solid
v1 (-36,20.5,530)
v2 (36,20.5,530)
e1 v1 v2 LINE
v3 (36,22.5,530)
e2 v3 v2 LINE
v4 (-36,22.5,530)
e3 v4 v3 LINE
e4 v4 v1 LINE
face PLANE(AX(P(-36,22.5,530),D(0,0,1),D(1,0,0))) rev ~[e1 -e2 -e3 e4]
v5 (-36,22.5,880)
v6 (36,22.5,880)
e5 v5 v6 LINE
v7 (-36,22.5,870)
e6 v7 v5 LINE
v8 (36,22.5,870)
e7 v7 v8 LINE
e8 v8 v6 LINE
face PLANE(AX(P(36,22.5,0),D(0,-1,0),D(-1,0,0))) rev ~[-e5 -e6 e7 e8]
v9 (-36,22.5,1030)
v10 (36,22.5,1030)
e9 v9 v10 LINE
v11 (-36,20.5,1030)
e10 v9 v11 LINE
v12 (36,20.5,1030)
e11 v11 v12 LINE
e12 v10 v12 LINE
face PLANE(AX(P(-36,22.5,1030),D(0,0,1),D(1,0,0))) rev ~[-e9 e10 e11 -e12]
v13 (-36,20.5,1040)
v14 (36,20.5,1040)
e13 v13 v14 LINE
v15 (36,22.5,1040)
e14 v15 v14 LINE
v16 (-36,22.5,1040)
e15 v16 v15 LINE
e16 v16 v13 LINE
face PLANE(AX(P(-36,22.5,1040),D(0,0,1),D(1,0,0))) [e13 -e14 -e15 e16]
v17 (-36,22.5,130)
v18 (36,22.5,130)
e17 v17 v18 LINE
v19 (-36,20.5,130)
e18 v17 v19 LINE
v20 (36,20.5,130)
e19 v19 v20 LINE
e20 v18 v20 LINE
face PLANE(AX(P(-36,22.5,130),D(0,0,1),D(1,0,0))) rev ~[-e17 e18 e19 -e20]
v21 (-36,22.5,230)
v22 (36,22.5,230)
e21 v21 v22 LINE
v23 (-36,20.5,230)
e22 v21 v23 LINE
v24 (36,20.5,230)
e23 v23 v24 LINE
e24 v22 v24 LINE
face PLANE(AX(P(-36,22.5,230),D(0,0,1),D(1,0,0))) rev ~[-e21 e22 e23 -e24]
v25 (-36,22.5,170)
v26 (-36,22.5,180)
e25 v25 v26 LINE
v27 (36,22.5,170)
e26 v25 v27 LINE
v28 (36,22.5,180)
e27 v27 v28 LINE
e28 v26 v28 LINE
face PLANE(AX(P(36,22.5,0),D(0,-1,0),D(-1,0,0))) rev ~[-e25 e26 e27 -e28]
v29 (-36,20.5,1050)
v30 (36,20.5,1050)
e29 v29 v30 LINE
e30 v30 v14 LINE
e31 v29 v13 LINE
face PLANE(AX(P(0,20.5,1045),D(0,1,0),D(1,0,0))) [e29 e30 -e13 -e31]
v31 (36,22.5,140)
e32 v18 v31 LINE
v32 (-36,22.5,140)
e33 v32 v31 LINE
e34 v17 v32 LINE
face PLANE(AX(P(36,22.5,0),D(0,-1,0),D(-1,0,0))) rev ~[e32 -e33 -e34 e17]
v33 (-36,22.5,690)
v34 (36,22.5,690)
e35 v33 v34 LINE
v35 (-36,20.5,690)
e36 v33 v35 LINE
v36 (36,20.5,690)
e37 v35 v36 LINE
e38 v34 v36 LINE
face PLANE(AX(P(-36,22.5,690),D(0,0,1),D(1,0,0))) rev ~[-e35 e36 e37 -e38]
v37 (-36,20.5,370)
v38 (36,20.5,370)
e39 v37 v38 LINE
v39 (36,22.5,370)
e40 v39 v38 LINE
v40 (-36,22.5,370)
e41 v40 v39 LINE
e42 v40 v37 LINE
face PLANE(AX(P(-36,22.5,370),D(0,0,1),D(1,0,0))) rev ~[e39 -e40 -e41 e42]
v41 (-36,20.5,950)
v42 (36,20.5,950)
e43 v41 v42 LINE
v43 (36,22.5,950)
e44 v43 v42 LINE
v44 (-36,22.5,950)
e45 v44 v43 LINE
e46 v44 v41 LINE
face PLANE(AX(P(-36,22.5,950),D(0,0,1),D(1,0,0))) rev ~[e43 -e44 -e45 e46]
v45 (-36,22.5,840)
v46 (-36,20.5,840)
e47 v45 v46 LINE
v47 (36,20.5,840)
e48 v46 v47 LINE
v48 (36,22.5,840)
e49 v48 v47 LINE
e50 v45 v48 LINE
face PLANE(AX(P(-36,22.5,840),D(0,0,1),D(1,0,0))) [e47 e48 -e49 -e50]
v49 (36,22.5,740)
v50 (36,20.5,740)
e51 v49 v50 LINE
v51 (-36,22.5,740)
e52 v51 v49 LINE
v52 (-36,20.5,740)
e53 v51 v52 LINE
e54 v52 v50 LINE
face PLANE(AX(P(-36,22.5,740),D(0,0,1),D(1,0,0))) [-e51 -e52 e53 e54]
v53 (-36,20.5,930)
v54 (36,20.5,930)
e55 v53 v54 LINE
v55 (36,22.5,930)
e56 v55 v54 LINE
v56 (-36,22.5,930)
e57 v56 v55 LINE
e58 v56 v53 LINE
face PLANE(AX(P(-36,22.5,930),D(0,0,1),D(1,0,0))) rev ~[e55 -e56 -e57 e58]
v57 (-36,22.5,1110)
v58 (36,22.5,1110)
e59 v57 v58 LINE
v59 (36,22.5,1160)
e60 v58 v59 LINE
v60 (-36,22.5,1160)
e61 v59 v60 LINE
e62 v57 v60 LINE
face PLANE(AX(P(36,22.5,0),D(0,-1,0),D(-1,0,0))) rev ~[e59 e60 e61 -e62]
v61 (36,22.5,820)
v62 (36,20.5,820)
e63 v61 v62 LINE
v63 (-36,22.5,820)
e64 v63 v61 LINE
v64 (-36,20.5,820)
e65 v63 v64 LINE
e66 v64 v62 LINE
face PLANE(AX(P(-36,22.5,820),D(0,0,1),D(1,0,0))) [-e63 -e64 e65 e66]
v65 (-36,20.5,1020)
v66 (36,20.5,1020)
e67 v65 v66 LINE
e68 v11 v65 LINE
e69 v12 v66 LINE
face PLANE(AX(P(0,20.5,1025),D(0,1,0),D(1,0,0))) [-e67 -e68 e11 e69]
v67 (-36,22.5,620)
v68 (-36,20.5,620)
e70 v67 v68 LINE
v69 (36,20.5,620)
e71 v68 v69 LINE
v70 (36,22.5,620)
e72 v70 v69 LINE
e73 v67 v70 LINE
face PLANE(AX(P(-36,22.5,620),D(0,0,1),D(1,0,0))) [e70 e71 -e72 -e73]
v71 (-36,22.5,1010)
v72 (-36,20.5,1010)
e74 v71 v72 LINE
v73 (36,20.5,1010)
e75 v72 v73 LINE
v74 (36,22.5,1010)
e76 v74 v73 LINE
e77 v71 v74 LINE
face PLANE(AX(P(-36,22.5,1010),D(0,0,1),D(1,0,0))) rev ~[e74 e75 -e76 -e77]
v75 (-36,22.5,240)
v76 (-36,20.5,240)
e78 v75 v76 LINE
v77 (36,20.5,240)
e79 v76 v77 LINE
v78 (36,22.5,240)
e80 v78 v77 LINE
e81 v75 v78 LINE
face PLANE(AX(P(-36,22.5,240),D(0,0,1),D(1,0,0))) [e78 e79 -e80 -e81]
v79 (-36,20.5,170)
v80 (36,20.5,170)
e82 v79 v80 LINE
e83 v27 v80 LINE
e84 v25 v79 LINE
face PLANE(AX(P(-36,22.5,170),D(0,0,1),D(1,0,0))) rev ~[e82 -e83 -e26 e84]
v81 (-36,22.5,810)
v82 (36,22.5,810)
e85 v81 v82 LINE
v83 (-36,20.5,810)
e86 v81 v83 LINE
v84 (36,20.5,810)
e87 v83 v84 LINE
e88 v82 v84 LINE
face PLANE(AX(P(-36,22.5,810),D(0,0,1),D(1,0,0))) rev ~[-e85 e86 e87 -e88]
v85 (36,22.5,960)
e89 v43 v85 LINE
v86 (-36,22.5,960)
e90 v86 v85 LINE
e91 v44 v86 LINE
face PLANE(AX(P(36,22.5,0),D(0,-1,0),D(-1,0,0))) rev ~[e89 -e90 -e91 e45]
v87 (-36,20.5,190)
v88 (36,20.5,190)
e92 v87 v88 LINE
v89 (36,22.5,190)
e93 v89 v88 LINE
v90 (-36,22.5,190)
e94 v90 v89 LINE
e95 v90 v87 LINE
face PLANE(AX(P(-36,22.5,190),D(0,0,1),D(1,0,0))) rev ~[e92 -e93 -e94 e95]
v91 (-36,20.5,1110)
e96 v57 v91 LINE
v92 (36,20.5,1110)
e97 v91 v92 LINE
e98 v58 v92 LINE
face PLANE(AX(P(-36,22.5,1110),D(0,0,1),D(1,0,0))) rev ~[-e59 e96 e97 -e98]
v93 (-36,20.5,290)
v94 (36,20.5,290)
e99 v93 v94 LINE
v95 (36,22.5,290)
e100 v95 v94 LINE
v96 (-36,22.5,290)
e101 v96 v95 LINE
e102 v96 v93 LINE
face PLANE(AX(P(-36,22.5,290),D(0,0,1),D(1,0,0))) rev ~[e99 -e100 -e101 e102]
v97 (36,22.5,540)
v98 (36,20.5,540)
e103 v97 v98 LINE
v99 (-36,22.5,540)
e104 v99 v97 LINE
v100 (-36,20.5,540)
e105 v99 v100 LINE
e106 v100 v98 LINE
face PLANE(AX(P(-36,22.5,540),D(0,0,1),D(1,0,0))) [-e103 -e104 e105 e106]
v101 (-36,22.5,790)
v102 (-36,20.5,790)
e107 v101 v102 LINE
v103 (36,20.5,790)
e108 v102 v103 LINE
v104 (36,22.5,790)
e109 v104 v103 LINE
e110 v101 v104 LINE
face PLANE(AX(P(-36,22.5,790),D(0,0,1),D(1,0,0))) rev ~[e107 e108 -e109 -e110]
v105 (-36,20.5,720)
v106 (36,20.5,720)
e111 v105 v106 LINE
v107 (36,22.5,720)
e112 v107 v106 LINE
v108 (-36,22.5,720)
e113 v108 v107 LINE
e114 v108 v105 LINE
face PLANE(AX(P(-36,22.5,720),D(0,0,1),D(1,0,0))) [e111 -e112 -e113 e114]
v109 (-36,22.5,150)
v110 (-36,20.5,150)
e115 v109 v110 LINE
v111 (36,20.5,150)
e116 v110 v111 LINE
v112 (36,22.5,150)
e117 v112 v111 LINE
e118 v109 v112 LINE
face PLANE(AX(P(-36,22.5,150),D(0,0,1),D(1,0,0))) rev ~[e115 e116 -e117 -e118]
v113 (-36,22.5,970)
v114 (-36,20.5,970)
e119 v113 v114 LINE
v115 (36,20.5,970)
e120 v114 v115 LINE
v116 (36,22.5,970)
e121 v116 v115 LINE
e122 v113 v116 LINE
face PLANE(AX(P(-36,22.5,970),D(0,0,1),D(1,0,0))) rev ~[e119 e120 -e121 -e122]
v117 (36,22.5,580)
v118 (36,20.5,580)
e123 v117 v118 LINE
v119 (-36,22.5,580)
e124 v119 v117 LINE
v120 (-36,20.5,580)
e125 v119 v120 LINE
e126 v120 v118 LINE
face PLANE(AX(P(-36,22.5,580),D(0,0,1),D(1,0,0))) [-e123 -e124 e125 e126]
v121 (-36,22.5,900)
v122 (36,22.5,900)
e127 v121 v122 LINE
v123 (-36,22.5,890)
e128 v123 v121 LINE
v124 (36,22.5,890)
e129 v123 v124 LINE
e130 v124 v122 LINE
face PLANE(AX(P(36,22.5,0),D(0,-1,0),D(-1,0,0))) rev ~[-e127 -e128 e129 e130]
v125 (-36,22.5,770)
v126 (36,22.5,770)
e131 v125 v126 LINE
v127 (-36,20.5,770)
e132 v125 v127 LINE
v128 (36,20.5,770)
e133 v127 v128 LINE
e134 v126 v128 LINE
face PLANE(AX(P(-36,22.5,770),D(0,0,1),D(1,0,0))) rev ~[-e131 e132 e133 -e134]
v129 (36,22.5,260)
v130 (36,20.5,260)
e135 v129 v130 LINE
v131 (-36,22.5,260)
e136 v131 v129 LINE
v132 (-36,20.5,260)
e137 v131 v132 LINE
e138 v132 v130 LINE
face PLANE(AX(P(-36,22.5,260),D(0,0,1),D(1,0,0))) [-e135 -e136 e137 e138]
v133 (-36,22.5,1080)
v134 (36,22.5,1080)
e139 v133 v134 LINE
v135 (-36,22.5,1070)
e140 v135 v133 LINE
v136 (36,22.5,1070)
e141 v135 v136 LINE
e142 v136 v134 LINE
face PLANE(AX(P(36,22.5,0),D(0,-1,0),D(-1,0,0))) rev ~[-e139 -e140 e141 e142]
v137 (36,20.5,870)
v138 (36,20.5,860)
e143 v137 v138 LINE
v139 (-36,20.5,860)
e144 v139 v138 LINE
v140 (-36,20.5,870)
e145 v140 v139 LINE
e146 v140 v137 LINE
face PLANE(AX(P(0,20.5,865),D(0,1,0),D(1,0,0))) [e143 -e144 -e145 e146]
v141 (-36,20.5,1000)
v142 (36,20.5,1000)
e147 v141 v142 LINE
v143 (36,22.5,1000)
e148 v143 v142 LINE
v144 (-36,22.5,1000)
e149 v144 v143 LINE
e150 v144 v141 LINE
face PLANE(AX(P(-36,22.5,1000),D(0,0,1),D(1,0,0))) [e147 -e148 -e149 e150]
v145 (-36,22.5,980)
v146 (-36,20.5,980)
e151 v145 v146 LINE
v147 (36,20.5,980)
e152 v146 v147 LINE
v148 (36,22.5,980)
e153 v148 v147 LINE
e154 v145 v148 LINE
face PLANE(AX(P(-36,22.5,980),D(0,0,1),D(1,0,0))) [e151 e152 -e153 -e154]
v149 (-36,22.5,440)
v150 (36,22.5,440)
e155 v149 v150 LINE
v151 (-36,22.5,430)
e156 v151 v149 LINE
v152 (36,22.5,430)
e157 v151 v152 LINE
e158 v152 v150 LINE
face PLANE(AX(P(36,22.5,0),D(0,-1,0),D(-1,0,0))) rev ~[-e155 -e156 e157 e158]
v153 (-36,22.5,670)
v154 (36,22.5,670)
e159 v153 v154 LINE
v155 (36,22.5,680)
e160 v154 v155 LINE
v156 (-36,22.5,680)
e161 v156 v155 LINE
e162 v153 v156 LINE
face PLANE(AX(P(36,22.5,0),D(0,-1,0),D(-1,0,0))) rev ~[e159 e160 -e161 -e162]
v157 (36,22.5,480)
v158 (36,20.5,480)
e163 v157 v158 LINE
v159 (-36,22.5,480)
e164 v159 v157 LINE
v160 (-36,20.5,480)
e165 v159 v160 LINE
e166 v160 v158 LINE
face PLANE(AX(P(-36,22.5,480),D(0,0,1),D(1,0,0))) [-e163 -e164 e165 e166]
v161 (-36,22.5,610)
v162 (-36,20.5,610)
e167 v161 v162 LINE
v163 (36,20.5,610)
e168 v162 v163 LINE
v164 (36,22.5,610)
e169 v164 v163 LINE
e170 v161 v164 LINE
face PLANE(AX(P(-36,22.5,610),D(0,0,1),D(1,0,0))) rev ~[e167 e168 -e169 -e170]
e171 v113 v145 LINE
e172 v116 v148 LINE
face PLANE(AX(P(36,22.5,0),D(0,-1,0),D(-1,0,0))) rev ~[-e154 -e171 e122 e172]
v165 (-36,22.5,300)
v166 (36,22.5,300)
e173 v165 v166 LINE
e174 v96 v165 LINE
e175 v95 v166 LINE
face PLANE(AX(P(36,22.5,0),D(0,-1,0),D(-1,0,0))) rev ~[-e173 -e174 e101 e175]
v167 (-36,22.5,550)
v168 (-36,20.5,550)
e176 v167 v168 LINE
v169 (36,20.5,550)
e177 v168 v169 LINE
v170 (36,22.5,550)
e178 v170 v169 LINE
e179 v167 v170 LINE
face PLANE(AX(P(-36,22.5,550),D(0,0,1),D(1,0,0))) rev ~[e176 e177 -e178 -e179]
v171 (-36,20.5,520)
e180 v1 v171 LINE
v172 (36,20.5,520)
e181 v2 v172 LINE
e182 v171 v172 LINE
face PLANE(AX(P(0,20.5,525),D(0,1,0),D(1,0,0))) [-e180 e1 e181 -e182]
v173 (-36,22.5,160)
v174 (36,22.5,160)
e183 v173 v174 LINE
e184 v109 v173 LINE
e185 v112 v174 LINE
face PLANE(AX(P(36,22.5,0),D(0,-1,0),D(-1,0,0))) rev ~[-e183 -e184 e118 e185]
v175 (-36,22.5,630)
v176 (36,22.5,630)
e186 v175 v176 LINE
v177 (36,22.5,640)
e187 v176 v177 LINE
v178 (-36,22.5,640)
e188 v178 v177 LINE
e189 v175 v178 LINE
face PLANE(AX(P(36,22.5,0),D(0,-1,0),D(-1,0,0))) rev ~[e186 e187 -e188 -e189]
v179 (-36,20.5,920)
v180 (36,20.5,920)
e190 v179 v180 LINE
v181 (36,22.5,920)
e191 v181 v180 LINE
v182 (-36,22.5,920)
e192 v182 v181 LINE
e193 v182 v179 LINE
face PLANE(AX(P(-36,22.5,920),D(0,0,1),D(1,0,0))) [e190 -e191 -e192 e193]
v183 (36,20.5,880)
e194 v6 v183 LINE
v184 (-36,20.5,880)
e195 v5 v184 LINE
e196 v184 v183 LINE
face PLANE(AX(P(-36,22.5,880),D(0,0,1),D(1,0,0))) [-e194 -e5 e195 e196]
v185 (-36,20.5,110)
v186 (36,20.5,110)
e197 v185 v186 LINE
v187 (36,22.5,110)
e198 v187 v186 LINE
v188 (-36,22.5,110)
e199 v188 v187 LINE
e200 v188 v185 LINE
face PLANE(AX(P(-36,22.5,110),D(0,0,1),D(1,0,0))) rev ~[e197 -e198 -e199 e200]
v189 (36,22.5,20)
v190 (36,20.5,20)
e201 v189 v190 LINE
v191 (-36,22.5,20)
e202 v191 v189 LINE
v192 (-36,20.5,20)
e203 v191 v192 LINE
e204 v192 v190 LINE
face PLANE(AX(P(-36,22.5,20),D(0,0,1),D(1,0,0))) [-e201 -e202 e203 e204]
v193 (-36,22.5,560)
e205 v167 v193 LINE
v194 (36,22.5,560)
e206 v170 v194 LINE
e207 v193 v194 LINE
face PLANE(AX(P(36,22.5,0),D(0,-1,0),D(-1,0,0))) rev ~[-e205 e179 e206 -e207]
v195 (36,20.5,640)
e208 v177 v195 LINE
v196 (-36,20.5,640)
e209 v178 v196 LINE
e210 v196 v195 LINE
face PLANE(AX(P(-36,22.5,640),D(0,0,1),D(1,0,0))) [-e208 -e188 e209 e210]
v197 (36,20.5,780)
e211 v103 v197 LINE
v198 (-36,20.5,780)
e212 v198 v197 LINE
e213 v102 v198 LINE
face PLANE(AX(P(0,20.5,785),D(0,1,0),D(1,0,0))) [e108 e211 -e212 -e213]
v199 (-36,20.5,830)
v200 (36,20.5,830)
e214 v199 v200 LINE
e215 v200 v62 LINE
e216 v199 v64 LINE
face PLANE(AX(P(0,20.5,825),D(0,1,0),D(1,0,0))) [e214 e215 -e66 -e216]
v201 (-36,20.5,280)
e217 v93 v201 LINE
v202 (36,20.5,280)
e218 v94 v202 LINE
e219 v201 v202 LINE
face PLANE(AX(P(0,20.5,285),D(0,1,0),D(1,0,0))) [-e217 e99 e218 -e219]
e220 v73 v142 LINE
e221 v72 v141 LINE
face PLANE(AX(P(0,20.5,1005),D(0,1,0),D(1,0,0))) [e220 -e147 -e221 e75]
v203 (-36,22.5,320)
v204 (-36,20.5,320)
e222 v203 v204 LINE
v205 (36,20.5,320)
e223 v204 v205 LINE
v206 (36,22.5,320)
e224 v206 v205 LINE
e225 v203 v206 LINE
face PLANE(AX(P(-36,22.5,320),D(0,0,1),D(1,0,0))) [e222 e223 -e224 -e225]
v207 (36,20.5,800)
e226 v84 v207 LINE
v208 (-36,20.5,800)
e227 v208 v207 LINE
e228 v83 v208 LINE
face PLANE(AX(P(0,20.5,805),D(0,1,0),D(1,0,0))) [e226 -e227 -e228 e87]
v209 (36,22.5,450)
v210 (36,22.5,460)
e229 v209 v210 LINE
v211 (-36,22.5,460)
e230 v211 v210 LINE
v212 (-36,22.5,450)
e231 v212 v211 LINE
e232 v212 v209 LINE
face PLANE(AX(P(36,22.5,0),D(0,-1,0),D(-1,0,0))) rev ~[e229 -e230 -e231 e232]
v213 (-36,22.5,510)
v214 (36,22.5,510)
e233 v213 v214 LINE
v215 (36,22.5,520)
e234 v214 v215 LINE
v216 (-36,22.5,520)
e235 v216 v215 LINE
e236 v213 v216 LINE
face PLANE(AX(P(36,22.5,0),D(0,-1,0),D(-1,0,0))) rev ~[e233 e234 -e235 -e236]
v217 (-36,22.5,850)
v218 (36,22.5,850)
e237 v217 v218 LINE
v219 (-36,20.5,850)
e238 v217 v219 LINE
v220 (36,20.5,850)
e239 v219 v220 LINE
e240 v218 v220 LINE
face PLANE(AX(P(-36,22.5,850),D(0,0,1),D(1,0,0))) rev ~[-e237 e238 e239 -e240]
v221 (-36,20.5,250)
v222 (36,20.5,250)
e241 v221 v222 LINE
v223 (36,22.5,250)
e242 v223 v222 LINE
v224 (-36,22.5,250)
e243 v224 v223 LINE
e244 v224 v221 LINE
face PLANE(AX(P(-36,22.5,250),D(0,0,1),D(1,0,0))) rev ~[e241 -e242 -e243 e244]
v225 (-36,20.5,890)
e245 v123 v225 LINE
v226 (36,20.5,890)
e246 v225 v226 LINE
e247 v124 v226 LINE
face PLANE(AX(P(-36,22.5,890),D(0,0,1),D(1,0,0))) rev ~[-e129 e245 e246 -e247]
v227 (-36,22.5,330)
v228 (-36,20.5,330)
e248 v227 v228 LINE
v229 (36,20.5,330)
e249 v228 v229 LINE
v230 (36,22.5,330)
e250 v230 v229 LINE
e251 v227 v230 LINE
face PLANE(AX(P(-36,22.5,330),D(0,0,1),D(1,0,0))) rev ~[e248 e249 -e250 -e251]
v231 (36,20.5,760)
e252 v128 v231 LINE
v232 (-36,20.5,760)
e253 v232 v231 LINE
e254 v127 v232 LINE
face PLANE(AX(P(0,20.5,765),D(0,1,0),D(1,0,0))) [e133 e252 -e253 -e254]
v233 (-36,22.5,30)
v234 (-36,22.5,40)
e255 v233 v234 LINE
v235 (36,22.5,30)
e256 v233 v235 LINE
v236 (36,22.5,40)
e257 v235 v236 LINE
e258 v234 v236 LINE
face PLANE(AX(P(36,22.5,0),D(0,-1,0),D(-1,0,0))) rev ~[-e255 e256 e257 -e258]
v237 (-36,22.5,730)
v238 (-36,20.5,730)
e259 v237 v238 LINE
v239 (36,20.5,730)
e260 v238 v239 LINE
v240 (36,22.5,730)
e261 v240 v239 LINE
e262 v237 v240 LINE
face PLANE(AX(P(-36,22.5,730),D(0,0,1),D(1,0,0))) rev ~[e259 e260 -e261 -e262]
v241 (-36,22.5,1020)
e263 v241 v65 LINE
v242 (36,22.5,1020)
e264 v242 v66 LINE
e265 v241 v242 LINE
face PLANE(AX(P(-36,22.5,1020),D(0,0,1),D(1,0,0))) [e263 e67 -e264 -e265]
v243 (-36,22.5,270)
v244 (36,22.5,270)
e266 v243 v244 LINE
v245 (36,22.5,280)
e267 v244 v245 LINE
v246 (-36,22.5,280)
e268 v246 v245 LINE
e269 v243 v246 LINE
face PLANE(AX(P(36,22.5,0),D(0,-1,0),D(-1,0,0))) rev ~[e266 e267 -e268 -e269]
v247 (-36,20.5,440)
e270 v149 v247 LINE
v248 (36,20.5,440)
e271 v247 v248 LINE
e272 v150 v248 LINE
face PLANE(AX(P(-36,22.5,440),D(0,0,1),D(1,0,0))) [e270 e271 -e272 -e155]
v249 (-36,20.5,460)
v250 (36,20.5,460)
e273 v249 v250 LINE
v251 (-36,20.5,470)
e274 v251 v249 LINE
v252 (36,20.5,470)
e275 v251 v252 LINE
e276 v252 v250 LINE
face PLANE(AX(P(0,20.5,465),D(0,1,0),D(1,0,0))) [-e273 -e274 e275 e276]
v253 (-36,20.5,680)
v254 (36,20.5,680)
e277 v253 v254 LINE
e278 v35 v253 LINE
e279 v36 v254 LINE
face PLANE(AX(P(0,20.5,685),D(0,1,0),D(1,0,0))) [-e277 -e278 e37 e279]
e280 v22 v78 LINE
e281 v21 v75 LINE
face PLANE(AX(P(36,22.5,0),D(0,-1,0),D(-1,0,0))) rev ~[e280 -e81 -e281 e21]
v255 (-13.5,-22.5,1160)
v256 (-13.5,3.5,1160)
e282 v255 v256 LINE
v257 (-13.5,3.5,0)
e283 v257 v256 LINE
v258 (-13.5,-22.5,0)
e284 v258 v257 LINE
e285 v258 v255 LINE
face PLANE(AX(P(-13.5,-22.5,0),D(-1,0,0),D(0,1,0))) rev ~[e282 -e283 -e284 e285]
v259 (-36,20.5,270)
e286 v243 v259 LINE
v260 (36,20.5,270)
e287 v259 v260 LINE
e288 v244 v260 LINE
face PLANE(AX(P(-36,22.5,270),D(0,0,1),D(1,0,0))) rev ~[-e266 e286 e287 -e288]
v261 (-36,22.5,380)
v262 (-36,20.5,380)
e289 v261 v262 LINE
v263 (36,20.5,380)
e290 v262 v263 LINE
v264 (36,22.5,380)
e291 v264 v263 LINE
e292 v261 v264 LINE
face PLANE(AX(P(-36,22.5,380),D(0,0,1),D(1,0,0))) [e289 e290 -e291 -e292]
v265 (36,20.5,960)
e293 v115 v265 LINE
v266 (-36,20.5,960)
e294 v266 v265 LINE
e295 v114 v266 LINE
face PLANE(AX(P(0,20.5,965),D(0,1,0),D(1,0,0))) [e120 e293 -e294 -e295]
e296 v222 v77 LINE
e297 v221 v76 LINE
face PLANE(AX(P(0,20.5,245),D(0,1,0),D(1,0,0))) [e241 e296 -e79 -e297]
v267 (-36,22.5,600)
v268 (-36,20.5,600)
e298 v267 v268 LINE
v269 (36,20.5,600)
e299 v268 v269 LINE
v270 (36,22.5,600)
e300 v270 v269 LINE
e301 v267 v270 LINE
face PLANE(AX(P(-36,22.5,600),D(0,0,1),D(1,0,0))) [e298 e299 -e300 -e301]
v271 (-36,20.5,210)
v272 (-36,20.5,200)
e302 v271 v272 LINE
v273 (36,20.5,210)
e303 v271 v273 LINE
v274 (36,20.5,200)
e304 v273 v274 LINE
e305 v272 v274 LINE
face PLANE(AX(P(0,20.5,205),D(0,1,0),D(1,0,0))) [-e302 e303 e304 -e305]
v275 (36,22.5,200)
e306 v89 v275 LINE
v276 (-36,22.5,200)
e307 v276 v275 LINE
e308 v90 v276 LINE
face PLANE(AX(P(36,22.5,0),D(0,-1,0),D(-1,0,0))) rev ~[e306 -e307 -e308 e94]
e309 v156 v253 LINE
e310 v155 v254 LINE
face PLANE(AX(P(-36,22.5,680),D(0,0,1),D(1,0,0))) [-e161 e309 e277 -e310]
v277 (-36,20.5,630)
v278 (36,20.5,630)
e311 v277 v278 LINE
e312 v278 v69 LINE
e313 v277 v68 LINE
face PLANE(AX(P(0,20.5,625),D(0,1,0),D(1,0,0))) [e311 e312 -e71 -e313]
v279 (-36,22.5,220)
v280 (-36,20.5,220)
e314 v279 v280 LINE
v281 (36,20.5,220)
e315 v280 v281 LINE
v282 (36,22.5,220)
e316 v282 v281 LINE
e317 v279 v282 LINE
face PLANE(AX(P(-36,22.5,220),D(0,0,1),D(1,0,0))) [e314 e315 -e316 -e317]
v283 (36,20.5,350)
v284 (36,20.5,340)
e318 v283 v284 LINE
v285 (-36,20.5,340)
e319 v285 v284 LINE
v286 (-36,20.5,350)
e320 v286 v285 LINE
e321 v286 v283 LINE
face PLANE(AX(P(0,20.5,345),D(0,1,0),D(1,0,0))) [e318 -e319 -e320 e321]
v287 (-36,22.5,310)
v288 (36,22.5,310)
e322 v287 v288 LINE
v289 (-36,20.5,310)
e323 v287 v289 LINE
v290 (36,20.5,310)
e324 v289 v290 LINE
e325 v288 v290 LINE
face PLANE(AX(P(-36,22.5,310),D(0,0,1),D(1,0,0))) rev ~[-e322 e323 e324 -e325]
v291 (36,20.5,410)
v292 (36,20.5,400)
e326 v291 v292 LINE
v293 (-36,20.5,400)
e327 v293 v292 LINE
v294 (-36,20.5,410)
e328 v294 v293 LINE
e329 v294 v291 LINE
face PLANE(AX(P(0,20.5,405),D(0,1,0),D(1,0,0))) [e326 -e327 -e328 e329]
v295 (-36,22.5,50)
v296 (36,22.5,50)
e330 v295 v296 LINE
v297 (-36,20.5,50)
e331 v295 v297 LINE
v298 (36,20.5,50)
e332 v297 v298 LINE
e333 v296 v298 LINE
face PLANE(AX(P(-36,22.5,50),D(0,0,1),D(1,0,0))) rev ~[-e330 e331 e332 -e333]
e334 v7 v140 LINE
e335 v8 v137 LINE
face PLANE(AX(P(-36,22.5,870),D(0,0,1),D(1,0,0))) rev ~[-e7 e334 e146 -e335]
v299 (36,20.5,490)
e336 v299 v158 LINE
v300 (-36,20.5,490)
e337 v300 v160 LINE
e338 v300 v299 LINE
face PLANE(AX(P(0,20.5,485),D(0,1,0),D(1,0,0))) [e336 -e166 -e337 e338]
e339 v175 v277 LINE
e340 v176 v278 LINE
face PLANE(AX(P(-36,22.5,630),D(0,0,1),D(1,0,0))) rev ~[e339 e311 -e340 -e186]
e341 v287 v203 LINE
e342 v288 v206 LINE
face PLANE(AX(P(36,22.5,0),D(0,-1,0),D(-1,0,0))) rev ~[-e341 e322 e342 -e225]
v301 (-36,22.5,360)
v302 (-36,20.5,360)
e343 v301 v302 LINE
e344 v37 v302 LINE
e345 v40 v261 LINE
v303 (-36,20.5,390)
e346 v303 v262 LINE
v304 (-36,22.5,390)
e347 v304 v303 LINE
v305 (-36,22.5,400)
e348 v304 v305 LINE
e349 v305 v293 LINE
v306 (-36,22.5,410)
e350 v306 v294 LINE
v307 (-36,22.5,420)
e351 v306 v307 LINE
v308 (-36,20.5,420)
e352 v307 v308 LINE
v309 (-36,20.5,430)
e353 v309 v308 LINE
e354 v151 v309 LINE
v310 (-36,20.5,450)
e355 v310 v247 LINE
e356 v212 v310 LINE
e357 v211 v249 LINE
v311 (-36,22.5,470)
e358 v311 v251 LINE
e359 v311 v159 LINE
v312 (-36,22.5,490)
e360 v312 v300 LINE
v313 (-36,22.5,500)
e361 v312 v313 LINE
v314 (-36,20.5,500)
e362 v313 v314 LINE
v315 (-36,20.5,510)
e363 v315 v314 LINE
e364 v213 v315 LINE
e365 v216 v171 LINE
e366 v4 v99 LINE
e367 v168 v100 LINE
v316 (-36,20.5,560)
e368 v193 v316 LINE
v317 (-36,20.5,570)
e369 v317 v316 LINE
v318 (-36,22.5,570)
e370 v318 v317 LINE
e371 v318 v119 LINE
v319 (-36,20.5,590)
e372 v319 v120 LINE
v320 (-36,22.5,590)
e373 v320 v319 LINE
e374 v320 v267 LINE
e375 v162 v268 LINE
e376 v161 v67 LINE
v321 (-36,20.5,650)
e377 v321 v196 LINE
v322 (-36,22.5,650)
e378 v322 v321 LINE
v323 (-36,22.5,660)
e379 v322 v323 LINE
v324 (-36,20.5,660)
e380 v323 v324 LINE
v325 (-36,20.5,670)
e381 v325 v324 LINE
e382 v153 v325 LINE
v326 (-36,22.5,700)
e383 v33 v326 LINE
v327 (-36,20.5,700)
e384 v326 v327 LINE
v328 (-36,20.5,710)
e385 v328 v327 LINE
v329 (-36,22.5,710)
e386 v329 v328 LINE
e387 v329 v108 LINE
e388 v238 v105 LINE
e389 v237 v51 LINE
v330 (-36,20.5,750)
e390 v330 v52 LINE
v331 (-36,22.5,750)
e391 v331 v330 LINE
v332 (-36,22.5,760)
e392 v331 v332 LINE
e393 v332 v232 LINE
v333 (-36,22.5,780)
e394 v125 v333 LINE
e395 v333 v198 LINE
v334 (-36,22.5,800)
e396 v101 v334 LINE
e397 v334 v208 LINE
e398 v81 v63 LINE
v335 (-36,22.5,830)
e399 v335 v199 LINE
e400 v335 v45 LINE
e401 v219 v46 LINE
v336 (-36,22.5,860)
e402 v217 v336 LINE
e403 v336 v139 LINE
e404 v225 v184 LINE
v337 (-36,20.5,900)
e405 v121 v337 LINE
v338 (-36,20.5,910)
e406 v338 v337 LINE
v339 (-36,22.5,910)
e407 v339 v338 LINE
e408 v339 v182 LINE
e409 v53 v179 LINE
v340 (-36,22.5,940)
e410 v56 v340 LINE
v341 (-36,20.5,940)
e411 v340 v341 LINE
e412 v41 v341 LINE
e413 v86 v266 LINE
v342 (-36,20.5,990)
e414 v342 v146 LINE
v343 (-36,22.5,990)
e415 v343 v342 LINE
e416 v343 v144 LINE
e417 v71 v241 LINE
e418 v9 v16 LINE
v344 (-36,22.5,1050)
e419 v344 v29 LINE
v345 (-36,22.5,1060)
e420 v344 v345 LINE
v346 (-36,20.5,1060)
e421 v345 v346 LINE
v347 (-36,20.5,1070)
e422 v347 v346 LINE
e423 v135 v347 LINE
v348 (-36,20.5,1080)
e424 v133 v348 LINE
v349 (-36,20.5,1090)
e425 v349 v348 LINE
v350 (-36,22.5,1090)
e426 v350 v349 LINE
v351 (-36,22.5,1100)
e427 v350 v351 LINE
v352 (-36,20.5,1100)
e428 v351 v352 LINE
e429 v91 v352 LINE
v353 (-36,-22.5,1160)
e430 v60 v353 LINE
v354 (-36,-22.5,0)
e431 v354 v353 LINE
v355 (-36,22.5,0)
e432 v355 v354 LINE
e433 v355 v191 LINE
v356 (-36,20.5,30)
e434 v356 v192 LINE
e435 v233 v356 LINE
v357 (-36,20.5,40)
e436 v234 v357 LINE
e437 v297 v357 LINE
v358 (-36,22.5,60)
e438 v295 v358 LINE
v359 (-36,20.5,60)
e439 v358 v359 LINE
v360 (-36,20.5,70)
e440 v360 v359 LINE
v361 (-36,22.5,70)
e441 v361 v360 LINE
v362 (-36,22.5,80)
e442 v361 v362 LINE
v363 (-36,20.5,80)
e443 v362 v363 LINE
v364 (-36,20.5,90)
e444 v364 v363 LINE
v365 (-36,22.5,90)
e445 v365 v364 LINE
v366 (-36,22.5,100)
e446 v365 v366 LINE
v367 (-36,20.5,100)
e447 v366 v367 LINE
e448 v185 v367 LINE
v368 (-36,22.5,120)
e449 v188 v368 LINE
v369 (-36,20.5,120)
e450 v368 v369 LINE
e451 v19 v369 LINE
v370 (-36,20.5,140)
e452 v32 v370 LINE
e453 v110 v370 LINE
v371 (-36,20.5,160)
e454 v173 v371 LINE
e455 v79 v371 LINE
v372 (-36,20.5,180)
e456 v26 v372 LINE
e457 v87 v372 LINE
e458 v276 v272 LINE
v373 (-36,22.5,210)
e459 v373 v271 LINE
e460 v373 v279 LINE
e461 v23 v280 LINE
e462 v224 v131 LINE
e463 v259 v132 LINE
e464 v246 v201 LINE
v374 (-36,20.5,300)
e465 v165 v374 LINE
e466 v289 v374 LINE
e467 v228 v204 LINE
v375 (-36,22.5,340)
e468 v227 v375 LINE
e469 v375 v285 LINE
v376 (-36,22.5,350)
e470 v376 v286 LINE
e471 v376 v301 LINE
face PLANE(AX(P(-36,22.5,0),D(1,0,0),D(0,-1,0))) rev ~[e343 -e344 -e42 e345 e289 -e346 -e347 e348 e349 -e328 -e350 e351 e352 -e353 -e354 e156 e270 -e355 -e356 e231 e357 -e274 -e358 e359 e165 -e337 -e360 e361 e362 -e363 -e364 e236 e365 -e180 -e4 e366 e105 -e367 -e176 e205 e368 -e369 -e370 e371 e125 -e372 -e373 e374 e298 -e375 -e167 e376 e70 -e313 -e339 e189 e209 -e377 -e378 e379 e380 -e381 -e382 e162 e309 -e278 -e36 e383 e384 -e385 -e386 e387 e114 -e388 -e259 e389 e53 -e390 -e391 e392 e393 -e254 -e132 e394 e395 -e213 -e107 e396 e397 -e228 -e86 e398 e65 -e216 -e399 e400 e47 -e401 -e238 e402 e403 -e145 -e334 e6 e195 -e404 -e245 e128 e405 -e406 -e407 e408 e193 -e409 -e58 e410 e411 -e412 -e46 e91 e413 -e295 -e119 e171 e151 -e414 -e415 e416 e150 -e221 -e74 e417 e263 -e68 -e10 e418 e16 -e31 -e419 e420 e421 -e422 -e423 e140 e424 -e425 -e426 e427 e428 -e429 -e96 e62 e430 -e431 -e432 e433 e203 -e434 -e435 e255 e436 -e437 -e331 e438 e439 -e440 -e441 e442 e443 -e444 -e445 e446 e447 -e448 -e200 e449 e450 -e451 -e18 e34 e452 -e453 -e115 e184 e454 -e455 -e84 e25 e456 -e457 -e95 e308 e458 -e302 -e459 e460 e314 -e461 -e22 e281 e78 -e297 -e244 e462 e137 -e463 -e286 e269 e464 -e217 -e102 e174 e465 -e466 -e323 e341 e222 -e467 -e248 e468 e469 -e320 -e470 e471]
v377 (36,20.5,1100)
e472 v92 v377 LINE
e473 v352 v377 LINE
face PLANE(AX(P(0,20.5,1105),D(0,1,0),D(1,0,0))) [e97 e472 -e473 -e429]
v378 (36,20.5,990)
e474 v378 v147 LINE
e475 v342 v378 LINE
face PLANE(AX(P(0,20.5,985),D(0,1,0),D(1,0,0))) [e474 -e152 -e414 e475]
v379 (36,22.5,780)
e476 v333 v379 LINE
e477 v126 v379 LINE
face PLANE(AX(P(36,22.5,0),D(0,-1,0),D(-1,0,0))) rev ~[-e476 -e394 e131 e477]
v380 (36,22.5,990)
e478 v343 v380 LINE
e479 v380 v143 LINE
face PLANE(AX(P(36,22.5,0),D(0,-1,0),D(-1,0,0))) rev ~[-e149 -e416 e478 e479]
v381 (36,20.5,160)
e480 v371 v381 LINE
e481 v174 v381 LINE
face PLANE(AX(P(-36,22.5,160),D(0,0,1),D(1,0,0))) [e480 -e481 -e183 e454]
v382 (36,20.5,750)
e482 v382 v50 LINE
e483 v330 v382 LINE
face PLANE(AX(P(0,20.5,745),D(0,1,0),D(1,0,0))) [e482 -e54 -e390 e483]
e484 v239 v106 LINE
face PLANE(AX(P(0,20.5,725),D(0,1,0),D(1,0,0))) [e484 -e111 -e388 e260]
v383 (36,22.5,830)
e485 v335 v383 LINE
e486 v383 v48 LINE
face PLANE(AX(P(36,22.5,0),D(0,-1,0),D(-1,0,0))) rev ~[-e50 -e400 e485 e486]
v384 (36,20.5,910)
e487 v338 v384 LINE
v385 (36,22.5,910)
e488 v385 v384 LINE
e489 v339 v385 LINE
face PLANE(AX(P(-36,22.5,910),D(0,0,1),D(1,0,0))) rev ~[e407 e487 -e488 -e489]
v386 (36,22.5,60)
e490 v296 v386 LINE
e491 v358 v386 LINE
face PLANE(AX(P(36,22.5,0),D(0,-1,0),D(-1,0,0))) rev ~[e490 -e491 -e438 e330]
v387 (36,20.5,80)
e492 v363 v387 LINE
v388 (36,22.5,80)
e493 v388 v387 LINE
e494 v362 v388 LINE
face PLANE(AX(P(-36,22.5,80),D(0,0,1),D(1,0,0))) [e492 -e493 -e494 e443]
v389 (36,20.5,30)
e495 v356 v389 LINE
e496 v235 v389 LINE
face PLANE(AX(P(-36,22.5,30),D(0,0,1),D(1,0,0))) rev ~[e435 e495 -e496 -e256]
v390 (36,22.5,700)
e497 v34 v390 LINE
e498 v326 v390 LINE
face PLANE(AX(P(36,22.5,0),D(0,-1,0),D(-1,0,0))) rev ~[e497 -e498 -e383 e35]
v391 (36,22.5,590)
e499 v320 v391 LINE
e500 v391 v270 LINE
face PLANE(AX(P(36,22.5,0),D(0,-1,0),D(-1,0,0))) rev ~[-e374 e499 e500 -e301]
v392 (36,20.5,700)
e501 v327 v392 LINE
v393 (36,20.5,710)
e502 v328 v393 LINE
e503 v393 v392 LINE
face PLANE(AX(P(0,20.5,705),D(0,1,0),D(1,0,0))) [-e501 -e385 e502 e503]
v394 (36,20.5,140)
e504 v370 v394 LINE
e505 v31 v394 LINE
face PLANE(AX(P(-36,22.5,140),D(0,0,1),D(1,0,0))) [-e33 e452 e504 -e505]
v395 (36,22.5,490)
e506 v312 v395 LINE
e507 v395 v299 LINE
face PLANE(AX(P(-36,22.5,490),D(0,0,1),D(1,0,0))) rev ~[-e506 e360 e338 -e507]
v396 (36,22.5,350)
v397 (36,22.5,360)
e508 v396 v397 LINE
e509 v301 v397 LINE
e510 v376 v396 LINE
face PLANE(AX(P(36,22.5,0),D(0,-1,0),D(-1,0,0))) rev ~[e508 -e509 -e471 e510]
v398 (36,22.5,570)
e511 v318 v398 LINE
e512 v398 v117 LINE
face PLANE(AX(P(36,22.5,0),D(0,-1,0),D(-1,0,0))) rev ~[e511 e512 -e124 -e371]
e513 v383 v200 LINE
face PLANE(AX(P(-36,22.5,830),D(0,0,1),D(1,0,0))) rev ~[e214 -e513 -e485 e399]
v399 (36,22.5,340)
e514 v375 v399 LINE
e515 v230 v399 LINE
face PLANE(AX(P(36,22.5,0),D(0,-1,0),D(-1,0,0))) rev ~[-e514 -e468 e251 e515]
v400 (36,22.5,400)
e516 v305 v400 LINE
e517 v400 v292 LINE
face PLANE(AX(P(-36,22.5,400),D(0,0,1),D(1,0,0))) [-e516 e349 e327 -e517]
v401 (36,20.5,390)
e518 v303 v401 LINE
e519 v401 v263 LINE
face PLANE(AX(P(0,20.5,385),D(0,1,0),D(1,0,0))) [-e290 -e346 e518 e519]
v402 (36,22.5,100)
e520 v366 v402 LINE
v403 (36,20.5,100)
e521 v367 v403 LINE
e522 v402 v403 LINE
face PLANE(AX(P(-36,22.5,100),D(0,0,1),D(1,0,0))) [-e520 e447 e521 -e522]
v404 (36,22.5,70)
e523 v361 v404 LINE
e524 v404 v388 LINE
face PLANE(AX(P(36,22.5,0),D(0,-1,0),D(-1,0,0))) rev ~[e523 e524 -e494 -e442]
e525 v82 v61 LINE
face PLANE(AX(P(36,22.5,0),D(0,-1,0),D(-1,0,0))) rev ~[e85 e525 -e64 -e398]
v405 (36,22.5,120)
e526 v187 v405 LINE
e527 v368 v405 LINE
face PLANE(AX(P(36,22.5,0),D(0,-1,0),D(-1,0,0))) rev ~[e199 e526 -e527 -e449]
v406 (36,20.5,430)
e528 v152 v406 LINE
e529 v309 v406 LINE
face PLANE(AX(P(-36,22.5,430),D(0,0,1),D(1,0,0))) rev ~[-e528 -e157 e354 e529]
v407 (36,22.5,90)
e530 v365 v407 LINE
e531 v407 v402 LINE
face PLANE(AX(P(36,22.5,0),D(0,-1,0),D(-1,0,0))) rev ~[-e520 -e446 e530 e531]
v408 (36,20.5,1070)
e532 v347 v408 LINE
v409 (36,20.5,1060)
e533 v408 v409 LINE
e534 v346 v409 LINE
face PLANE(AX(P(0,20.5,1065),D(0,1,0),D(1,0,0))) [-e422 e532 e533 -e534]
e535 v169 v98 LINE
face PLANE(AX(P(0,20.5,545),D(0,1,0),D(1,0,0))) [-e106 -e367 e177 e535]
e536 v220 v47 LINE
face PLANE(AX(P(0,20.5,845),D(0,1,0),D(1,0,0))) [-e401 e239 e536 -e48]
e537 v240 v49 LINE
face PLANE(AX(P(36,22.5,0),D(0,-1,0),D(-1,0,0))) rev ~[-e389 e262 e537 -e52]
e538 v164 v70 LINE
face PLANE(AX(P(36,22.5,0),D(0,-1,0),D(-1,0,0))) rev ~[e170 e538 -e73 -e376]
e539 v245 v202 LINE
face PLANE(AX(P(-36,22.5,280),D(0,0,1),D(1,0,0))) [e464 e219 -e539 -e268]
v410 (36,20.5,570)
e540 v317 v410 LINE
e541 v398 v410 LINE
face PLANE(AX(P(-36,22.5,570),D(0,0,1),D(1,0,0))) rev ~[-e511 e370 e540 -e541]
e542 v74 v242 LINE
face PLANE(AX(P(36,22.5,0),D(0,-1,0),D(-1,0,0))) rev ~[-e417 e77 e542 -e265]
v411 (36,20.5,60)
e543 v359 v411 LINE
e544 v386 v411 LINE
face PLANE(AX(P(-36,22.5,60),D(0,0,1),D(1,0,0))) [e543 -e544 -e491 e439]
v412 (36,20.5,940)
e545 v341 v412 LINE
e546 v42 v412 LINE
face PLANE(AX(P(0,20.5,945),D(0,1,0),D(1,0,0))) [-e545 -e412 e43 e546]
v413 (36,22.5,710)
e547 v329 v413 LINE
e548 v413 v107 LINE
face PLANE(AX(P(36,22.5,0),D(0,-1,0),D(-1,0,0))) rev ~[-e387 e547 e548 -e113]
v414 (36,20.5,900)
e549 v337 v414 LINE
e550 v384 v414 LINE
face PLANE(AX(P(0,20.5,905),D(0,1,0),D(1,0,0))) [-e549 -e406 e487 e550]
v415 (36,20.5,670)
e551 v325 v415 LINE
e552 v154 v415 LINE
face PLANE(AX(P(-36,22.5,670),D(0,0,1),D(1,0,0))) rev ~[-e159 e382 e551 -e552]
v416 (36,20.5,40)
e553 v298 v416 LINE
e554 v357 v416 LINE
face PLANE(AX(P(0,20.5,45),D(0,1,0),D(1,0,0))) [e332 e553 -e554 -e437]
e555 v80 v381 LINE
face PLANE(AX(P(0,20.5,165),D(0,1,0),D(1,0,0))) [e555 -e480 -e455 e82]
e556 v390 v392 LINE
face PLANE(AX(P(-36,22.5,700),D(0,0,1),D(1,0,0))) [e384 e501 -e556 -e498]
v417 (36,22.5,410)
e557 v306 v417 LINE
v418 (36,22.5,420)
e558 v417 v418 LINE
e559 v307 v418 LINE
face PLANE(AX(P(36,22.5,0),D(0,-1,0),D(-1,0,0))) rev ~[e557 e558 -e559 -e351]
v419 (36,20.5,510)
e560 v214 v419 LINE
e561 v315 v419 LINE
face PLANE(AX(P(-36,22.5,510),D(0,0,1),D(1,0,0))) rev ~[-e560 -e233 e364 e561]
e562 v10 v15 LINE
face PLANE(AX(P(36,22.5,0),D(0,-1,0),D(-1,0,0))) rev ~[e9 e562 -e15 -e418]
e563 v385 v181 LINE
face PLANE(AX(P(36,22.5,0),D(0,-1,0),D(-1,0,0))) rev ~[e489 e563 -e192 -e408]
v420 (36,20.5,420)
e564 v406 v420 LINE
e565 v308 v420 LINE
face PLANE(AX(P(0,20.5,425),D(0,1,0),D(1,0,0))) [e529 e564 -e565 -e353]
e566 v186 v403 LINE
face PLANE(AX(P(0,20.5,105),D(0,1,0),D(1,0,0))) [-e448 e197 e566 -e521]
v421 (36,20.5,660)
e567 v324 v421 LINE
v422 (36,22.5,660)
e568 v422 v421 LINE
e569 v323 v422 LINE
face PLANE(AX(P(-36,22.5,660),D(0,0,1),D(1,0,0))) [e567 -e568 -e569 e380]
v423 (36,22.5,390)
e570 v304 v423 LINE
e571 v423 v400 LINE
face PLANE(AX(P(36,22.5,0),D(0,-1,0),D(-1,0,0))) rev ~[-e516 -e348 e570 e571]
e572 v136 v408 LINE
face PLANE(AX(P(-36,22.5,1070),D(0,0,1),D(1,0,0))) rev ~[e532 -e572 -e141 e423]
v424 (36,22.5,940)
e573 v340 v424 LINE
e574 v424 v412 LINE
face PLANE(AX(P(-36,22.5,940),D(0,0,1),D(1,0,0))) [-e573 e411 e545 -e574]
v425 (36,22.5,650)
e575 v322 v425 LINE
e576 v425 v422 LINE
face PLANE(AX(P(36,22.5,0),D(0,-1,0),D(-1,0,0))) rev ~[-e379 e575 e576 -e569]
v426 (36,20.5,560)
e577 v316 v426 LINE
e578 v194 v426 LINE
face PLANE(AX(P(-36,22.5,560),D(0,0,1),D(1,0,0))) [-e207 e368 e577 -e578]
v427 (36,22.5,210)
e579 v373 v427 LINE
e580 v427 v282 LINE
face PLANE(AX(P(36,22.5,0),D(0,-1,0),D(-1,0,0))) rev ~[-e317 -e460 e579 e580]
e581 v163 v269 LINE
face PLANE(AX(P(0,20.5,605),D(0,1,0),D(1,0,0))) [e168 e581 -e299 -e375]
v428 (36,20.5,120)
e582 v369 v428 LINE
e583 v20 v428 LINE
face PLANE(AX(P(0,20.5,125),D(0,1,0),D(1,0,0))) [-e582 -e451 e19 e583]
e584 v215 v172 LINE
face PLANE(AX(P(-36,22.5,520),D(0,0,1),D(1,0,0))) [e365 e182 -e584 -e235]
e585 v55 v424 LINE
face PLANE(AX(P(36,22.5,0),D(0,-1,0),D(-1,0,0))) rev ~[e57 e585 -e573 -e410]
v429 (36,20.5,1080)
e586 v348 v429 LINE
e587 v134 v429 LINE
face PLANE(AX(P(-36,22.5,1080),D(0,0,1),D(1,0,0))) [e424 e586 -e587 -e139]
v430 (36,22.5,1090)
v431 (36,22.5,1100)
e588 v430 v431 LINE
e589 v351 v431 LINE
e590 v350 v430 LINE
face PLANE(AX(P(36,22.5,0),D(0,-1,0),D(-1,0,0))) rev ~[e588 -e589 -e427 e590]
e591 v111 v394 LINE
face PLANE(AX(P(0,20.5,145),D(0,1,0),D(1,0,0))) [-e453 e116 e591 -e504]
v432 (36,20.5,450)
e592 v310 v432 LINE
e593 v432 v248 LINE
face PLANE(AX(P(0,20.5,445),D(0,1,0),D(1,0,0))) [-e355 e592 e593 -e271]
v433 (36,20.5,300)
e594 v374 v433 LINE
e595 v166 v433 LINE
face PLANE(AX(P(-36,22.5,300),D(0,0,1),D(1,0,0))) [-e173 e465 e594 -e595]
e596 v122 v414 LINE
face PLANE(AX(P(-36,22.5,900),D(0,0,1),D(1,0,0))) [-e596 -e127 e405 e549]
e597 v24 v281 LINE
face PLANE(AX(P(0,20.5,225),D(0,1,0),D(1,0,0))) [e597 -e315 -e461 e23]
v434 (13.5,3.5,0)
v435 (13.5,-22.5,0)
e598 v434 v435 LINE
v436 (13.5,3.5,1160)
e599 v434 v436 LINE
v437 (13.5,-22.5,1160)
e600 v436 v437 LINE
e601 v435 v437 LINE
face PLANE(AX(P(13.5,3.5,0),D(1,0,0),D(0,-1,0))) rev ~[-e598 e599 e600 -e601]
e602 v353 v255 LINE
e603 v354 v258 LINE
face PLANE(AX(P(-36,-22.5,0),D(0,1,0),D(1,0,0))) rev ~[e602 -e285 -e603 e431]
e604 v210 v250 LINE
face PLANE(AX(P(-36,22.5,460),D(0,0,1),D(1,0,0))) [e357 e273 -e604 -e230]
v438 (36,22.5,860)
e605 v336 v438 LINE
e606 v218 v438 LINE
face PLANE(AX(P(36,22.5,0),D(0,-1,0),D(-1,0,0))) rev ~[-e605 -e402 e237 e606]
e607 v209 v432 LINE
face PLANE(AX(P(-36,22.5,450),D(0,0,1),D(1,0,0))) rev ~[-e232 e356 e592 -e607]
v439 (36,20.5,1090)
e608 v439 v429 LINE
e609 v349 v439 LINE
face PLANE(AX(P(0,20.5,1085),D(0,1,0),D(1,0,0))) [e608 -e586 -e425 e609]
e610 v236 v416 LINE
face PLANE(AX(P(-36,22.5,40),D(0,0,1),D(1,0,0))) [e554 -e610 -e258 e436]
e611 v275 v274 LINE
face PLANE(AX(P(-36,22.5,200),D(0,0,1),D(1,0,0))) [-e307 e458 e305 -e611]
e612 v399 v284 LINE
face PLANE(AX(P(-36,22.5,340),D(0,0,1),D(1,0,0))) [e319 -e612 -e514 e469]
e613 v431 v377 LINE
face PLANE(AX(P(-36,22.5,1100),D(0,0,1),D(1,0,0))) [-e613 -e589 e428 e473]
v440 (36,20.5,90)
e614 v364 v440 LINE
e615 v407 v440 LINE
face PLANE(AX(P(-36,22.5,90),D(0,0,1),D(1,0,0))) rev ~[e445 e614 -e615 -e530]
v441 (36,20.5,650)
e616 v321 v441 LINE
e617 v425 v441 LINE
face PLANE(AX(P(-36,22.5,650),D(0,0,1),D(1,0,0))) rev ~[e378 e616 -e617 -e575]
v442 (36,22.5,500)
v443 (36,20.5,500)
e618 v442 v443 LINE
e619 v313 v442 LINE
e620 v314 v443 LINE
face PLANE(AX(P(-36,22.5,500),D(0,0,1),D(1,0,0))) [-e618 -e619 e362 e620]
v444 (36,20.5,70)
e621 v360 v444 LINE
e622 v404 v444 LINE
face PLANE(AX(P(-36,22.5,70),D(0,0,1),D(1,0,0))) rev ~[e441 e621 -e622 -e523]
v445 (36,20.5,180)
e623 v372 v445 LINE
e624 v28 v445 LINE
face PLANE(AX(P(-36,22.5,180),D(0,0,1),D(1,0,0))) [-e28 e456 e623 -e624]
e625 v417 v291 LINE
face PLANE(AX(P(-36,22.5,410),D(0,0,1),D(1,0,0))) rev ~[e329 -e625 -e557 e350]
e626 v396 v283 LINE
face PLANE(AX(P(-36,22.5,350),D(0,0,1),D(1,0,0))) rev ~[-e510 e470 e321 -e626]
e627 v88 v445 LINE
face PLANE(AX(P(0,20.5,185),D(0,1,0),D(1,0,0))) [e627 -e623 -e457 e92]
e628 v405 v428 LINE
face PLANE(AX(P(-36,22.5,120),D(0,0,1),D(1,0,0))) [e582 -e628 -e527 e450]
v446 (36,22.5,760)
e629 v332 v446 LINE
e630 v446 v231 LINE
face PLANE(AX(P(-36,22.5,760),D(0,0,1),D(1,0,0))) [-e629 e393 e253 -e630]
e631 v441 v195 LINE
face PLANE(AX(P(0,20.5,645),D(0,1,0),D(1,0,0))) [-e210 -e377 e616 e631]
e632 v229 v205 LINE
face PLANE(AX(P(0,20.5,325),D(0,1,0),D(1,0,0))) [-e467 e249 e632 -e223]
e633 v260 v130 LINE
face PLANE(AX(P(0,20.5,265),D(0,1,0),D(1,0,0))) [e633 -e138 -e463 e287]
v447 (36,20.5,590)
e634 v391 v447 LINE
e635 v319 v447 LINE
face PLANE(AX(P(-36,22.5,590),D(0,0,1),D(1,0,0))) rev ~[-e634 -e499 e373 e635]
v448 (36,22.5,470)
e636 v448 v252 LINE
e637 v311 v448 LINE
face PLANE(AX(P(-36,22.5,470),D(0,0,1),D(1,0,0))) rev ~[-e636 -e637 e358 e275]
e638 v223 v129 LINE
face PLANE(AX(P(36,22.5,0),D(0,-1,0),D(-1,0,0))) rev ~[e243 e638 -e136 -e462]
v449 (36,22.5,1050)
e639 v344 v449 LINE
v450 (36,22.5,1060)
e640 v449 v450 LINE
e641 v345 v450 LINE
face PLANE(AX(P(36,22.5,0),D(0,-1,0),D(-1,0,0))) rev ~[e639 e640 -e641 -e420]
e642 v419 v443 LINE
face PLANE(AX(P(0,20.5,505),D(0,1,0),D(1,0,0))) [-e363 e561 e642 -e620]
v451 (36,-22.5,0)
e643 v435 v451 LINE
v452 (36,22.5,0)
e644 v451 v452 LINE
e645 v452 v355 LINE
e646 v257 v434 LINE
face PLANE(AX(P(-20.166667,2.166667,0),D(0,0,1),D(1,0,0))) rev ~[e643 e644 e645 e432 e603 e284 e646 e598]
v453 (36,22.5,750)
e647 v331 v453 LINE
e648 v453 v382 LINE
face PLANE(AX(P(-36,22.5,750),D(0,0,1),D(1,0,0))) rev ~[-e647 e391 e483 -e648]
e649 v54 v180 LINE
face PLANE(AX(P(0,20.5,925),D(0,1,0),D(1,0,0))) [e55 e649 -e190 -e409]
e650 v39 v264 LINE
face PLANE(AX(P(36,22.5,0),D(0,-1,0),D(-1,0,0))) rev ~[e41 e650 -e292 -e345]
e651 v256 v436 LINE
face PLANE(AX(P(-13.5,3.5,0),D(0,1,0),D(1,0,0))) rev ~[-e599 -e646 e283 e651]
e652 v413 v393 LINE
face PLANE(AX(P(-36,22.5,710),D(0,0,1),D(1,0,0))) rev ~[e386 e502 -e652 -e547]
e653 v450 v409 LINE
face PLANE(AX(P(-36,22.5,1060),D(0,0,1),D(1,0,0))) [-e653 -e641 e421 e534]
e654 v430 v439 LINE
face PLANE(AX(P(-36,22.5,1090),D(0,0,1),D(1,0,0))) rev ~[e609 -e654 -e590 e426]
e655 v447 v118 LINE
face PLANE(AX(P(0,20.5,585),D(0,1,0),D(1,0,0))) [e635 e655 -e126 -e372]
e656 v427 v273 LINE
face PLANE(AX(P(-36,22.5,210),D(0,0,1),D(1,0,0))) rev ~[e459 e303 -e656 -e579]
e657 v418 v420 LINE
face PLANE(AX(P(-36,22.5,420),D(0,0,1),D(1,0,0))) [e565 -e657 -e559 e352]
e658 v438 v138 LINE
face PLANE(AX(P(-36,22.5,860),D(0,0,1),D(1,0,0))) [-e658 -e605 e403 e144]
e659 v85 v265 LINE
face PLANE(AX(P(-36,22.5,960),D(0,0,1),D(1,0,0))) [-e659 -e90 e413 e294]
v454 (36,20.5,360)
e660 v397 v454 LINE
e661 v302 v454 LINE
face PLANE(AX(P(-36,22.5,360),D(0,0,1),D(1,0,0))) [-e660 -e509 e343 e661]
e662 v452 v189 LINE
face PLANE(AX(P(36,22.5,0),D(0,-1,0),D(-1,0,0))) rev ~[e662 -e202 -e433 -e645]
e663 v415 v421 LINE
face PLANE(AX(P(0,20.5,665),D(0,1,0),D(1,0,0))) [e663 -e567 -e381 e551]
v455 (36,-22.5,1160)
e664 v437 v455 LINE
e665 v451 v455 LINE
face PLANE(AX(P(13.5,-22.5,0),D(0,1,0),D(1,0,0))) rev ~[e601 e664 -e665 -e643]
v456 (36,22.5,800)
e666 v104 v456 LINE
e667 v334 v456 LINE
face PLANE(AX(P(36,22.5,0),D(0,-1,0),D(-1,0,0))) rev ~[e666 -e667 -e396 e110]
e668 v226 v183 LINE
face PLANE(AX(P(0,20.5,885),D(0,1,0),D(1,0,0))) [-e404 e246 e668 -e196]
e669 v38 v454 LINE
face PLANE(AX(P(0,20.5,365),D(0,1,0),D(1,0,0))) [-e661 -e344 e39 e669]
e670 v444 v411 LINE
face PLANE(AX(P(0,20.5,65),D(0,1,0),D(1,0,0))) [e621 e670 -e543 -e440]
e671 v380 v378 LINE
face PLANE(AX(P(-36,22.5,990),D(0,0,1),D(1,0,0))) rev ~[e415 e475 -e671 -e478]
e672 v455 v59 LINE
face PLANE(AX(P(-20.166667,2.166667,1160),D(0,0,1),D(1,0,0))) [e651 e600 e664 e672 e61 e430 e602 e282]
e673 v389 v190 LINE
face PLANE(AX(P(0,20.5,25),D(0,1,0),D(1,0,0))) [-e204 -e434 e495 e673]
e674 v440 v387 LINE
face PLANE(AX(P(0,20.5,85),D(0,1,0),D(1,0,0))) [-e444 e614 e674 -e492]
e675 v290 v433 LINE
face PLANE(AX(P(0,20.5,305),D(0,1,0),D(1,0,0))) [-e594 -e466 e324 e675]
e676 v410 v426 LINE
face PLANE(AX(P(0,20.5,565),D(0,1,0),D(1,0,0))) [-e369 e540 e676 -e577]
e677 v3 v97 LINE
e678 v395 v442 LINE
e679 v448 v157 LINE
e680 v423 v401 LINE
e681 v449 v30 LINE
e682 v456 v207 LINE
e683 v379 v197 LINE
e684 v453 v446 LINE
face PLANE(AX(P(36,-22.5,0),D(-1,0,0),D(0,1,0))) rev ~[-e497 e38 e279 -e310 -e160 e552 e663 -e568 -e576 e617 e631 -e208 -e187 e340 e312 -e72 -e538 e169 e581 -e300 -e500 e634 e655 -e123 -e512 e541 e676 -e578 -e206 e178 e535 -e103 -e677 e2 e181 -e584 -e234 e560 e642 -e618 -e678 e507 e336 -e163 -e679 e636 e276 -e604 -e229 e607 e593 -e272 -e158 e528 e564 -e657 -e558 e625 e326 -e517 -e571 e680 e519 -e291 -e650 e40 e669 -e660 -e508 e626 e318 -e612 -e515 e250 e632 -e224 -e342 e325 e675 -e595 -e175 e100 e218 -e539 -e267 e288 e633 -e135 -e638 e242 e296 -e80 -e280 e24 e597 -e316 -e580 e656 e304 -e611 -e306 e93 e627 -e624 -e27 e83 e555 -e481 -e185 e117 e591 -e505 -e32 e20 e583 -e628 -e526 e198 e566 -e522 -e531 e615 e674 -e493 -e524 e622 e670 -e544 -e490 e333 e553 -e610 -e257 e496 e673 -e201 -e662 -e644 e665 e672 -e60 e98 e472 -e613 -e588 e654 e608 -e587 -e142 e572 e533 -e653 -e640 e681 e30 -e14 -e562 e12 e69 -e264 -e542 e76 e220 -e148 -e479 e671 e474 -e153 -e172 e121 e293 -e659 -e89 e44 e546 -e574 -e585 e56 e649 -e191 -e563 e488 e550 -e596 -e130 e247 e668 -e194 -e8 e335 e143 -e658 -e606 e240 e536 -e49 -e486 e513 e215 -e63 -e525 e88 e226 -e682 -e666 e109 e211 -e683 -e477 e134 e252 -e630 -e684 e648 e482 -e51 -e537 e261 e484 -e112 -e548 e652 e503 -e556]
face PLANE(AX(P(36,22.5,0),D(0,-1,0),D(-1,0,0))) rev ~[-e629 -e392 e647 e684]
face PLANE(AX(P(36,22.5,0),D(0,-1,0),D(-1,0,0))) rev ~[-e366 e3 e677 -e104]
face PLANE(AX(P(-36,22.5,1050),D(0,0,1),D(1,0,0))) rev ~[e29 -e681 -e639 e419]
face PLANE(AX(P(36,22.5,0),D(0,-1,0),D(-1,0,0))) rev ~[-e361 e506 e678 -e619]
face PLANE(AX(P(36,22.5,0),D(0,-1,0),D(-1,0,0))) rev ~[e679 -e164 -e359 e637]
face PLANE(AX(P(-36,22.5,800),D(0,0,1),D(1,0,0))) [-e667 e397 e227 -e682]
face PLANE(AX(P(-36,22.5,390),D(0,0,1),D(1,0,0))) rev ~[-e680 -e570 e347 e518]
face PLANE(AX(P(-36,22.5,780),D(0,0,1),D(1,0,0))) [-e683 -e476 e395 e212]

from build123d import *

# Parameters (mm, degrees)
BOSS_EXTRUDE1_DEPTH = 1160
SKETCH2_W           = 72
SKETCH2_H           = 10
CUT_EXTRUDE1_DEPTH  = 2
LPATTERN1_COUNT     = 55
LPATTERN1_PITCH     = 20


with BuildPart() as part:
    # Sketch1 → Boss-Extrude1 (new body)
    with BuildSketch(Plane.XY):
        Polygon((0, 3.5), (0, 22.5), (-36, 22.5), (-36, -22.5), (-13.5, -22.5), (-13.5, 3.5), align=None)
        Polygon((36, 22.5), (0, 22.5), (0, 3.5), (13.5, 3.5), (13.5, -22.5), (36, -22.5), align=None)
    extrude(amount=BOSS_EXTRUDE1_DEPTH)

    # Sketch2 → Cut-Extrude1 (cut)
    with BuildSketch(Plane(origin=(0, 22.5, 0), x_dir=(1, 0, 0), z_dir=(0, 1, 0))):
        with Locations((0, -25)):
            Rectangle(SKETCH2_W, SKETCH2_H)
    cut_extrude1 = extrude(amount=-CUT_EXTRUDE1_DEPTH, mode=Mode.SUBTRACT)

    # LPattern1: Cut-Extrude1 ×55
    with Locations(*[(0, 0, i * LPATTERN1_PITCH) for i in range(1, LPATTERN1_COUNT)]):
        add(cut_extrude1, mode=Mode.SUBTRACT)


solid = part.part
